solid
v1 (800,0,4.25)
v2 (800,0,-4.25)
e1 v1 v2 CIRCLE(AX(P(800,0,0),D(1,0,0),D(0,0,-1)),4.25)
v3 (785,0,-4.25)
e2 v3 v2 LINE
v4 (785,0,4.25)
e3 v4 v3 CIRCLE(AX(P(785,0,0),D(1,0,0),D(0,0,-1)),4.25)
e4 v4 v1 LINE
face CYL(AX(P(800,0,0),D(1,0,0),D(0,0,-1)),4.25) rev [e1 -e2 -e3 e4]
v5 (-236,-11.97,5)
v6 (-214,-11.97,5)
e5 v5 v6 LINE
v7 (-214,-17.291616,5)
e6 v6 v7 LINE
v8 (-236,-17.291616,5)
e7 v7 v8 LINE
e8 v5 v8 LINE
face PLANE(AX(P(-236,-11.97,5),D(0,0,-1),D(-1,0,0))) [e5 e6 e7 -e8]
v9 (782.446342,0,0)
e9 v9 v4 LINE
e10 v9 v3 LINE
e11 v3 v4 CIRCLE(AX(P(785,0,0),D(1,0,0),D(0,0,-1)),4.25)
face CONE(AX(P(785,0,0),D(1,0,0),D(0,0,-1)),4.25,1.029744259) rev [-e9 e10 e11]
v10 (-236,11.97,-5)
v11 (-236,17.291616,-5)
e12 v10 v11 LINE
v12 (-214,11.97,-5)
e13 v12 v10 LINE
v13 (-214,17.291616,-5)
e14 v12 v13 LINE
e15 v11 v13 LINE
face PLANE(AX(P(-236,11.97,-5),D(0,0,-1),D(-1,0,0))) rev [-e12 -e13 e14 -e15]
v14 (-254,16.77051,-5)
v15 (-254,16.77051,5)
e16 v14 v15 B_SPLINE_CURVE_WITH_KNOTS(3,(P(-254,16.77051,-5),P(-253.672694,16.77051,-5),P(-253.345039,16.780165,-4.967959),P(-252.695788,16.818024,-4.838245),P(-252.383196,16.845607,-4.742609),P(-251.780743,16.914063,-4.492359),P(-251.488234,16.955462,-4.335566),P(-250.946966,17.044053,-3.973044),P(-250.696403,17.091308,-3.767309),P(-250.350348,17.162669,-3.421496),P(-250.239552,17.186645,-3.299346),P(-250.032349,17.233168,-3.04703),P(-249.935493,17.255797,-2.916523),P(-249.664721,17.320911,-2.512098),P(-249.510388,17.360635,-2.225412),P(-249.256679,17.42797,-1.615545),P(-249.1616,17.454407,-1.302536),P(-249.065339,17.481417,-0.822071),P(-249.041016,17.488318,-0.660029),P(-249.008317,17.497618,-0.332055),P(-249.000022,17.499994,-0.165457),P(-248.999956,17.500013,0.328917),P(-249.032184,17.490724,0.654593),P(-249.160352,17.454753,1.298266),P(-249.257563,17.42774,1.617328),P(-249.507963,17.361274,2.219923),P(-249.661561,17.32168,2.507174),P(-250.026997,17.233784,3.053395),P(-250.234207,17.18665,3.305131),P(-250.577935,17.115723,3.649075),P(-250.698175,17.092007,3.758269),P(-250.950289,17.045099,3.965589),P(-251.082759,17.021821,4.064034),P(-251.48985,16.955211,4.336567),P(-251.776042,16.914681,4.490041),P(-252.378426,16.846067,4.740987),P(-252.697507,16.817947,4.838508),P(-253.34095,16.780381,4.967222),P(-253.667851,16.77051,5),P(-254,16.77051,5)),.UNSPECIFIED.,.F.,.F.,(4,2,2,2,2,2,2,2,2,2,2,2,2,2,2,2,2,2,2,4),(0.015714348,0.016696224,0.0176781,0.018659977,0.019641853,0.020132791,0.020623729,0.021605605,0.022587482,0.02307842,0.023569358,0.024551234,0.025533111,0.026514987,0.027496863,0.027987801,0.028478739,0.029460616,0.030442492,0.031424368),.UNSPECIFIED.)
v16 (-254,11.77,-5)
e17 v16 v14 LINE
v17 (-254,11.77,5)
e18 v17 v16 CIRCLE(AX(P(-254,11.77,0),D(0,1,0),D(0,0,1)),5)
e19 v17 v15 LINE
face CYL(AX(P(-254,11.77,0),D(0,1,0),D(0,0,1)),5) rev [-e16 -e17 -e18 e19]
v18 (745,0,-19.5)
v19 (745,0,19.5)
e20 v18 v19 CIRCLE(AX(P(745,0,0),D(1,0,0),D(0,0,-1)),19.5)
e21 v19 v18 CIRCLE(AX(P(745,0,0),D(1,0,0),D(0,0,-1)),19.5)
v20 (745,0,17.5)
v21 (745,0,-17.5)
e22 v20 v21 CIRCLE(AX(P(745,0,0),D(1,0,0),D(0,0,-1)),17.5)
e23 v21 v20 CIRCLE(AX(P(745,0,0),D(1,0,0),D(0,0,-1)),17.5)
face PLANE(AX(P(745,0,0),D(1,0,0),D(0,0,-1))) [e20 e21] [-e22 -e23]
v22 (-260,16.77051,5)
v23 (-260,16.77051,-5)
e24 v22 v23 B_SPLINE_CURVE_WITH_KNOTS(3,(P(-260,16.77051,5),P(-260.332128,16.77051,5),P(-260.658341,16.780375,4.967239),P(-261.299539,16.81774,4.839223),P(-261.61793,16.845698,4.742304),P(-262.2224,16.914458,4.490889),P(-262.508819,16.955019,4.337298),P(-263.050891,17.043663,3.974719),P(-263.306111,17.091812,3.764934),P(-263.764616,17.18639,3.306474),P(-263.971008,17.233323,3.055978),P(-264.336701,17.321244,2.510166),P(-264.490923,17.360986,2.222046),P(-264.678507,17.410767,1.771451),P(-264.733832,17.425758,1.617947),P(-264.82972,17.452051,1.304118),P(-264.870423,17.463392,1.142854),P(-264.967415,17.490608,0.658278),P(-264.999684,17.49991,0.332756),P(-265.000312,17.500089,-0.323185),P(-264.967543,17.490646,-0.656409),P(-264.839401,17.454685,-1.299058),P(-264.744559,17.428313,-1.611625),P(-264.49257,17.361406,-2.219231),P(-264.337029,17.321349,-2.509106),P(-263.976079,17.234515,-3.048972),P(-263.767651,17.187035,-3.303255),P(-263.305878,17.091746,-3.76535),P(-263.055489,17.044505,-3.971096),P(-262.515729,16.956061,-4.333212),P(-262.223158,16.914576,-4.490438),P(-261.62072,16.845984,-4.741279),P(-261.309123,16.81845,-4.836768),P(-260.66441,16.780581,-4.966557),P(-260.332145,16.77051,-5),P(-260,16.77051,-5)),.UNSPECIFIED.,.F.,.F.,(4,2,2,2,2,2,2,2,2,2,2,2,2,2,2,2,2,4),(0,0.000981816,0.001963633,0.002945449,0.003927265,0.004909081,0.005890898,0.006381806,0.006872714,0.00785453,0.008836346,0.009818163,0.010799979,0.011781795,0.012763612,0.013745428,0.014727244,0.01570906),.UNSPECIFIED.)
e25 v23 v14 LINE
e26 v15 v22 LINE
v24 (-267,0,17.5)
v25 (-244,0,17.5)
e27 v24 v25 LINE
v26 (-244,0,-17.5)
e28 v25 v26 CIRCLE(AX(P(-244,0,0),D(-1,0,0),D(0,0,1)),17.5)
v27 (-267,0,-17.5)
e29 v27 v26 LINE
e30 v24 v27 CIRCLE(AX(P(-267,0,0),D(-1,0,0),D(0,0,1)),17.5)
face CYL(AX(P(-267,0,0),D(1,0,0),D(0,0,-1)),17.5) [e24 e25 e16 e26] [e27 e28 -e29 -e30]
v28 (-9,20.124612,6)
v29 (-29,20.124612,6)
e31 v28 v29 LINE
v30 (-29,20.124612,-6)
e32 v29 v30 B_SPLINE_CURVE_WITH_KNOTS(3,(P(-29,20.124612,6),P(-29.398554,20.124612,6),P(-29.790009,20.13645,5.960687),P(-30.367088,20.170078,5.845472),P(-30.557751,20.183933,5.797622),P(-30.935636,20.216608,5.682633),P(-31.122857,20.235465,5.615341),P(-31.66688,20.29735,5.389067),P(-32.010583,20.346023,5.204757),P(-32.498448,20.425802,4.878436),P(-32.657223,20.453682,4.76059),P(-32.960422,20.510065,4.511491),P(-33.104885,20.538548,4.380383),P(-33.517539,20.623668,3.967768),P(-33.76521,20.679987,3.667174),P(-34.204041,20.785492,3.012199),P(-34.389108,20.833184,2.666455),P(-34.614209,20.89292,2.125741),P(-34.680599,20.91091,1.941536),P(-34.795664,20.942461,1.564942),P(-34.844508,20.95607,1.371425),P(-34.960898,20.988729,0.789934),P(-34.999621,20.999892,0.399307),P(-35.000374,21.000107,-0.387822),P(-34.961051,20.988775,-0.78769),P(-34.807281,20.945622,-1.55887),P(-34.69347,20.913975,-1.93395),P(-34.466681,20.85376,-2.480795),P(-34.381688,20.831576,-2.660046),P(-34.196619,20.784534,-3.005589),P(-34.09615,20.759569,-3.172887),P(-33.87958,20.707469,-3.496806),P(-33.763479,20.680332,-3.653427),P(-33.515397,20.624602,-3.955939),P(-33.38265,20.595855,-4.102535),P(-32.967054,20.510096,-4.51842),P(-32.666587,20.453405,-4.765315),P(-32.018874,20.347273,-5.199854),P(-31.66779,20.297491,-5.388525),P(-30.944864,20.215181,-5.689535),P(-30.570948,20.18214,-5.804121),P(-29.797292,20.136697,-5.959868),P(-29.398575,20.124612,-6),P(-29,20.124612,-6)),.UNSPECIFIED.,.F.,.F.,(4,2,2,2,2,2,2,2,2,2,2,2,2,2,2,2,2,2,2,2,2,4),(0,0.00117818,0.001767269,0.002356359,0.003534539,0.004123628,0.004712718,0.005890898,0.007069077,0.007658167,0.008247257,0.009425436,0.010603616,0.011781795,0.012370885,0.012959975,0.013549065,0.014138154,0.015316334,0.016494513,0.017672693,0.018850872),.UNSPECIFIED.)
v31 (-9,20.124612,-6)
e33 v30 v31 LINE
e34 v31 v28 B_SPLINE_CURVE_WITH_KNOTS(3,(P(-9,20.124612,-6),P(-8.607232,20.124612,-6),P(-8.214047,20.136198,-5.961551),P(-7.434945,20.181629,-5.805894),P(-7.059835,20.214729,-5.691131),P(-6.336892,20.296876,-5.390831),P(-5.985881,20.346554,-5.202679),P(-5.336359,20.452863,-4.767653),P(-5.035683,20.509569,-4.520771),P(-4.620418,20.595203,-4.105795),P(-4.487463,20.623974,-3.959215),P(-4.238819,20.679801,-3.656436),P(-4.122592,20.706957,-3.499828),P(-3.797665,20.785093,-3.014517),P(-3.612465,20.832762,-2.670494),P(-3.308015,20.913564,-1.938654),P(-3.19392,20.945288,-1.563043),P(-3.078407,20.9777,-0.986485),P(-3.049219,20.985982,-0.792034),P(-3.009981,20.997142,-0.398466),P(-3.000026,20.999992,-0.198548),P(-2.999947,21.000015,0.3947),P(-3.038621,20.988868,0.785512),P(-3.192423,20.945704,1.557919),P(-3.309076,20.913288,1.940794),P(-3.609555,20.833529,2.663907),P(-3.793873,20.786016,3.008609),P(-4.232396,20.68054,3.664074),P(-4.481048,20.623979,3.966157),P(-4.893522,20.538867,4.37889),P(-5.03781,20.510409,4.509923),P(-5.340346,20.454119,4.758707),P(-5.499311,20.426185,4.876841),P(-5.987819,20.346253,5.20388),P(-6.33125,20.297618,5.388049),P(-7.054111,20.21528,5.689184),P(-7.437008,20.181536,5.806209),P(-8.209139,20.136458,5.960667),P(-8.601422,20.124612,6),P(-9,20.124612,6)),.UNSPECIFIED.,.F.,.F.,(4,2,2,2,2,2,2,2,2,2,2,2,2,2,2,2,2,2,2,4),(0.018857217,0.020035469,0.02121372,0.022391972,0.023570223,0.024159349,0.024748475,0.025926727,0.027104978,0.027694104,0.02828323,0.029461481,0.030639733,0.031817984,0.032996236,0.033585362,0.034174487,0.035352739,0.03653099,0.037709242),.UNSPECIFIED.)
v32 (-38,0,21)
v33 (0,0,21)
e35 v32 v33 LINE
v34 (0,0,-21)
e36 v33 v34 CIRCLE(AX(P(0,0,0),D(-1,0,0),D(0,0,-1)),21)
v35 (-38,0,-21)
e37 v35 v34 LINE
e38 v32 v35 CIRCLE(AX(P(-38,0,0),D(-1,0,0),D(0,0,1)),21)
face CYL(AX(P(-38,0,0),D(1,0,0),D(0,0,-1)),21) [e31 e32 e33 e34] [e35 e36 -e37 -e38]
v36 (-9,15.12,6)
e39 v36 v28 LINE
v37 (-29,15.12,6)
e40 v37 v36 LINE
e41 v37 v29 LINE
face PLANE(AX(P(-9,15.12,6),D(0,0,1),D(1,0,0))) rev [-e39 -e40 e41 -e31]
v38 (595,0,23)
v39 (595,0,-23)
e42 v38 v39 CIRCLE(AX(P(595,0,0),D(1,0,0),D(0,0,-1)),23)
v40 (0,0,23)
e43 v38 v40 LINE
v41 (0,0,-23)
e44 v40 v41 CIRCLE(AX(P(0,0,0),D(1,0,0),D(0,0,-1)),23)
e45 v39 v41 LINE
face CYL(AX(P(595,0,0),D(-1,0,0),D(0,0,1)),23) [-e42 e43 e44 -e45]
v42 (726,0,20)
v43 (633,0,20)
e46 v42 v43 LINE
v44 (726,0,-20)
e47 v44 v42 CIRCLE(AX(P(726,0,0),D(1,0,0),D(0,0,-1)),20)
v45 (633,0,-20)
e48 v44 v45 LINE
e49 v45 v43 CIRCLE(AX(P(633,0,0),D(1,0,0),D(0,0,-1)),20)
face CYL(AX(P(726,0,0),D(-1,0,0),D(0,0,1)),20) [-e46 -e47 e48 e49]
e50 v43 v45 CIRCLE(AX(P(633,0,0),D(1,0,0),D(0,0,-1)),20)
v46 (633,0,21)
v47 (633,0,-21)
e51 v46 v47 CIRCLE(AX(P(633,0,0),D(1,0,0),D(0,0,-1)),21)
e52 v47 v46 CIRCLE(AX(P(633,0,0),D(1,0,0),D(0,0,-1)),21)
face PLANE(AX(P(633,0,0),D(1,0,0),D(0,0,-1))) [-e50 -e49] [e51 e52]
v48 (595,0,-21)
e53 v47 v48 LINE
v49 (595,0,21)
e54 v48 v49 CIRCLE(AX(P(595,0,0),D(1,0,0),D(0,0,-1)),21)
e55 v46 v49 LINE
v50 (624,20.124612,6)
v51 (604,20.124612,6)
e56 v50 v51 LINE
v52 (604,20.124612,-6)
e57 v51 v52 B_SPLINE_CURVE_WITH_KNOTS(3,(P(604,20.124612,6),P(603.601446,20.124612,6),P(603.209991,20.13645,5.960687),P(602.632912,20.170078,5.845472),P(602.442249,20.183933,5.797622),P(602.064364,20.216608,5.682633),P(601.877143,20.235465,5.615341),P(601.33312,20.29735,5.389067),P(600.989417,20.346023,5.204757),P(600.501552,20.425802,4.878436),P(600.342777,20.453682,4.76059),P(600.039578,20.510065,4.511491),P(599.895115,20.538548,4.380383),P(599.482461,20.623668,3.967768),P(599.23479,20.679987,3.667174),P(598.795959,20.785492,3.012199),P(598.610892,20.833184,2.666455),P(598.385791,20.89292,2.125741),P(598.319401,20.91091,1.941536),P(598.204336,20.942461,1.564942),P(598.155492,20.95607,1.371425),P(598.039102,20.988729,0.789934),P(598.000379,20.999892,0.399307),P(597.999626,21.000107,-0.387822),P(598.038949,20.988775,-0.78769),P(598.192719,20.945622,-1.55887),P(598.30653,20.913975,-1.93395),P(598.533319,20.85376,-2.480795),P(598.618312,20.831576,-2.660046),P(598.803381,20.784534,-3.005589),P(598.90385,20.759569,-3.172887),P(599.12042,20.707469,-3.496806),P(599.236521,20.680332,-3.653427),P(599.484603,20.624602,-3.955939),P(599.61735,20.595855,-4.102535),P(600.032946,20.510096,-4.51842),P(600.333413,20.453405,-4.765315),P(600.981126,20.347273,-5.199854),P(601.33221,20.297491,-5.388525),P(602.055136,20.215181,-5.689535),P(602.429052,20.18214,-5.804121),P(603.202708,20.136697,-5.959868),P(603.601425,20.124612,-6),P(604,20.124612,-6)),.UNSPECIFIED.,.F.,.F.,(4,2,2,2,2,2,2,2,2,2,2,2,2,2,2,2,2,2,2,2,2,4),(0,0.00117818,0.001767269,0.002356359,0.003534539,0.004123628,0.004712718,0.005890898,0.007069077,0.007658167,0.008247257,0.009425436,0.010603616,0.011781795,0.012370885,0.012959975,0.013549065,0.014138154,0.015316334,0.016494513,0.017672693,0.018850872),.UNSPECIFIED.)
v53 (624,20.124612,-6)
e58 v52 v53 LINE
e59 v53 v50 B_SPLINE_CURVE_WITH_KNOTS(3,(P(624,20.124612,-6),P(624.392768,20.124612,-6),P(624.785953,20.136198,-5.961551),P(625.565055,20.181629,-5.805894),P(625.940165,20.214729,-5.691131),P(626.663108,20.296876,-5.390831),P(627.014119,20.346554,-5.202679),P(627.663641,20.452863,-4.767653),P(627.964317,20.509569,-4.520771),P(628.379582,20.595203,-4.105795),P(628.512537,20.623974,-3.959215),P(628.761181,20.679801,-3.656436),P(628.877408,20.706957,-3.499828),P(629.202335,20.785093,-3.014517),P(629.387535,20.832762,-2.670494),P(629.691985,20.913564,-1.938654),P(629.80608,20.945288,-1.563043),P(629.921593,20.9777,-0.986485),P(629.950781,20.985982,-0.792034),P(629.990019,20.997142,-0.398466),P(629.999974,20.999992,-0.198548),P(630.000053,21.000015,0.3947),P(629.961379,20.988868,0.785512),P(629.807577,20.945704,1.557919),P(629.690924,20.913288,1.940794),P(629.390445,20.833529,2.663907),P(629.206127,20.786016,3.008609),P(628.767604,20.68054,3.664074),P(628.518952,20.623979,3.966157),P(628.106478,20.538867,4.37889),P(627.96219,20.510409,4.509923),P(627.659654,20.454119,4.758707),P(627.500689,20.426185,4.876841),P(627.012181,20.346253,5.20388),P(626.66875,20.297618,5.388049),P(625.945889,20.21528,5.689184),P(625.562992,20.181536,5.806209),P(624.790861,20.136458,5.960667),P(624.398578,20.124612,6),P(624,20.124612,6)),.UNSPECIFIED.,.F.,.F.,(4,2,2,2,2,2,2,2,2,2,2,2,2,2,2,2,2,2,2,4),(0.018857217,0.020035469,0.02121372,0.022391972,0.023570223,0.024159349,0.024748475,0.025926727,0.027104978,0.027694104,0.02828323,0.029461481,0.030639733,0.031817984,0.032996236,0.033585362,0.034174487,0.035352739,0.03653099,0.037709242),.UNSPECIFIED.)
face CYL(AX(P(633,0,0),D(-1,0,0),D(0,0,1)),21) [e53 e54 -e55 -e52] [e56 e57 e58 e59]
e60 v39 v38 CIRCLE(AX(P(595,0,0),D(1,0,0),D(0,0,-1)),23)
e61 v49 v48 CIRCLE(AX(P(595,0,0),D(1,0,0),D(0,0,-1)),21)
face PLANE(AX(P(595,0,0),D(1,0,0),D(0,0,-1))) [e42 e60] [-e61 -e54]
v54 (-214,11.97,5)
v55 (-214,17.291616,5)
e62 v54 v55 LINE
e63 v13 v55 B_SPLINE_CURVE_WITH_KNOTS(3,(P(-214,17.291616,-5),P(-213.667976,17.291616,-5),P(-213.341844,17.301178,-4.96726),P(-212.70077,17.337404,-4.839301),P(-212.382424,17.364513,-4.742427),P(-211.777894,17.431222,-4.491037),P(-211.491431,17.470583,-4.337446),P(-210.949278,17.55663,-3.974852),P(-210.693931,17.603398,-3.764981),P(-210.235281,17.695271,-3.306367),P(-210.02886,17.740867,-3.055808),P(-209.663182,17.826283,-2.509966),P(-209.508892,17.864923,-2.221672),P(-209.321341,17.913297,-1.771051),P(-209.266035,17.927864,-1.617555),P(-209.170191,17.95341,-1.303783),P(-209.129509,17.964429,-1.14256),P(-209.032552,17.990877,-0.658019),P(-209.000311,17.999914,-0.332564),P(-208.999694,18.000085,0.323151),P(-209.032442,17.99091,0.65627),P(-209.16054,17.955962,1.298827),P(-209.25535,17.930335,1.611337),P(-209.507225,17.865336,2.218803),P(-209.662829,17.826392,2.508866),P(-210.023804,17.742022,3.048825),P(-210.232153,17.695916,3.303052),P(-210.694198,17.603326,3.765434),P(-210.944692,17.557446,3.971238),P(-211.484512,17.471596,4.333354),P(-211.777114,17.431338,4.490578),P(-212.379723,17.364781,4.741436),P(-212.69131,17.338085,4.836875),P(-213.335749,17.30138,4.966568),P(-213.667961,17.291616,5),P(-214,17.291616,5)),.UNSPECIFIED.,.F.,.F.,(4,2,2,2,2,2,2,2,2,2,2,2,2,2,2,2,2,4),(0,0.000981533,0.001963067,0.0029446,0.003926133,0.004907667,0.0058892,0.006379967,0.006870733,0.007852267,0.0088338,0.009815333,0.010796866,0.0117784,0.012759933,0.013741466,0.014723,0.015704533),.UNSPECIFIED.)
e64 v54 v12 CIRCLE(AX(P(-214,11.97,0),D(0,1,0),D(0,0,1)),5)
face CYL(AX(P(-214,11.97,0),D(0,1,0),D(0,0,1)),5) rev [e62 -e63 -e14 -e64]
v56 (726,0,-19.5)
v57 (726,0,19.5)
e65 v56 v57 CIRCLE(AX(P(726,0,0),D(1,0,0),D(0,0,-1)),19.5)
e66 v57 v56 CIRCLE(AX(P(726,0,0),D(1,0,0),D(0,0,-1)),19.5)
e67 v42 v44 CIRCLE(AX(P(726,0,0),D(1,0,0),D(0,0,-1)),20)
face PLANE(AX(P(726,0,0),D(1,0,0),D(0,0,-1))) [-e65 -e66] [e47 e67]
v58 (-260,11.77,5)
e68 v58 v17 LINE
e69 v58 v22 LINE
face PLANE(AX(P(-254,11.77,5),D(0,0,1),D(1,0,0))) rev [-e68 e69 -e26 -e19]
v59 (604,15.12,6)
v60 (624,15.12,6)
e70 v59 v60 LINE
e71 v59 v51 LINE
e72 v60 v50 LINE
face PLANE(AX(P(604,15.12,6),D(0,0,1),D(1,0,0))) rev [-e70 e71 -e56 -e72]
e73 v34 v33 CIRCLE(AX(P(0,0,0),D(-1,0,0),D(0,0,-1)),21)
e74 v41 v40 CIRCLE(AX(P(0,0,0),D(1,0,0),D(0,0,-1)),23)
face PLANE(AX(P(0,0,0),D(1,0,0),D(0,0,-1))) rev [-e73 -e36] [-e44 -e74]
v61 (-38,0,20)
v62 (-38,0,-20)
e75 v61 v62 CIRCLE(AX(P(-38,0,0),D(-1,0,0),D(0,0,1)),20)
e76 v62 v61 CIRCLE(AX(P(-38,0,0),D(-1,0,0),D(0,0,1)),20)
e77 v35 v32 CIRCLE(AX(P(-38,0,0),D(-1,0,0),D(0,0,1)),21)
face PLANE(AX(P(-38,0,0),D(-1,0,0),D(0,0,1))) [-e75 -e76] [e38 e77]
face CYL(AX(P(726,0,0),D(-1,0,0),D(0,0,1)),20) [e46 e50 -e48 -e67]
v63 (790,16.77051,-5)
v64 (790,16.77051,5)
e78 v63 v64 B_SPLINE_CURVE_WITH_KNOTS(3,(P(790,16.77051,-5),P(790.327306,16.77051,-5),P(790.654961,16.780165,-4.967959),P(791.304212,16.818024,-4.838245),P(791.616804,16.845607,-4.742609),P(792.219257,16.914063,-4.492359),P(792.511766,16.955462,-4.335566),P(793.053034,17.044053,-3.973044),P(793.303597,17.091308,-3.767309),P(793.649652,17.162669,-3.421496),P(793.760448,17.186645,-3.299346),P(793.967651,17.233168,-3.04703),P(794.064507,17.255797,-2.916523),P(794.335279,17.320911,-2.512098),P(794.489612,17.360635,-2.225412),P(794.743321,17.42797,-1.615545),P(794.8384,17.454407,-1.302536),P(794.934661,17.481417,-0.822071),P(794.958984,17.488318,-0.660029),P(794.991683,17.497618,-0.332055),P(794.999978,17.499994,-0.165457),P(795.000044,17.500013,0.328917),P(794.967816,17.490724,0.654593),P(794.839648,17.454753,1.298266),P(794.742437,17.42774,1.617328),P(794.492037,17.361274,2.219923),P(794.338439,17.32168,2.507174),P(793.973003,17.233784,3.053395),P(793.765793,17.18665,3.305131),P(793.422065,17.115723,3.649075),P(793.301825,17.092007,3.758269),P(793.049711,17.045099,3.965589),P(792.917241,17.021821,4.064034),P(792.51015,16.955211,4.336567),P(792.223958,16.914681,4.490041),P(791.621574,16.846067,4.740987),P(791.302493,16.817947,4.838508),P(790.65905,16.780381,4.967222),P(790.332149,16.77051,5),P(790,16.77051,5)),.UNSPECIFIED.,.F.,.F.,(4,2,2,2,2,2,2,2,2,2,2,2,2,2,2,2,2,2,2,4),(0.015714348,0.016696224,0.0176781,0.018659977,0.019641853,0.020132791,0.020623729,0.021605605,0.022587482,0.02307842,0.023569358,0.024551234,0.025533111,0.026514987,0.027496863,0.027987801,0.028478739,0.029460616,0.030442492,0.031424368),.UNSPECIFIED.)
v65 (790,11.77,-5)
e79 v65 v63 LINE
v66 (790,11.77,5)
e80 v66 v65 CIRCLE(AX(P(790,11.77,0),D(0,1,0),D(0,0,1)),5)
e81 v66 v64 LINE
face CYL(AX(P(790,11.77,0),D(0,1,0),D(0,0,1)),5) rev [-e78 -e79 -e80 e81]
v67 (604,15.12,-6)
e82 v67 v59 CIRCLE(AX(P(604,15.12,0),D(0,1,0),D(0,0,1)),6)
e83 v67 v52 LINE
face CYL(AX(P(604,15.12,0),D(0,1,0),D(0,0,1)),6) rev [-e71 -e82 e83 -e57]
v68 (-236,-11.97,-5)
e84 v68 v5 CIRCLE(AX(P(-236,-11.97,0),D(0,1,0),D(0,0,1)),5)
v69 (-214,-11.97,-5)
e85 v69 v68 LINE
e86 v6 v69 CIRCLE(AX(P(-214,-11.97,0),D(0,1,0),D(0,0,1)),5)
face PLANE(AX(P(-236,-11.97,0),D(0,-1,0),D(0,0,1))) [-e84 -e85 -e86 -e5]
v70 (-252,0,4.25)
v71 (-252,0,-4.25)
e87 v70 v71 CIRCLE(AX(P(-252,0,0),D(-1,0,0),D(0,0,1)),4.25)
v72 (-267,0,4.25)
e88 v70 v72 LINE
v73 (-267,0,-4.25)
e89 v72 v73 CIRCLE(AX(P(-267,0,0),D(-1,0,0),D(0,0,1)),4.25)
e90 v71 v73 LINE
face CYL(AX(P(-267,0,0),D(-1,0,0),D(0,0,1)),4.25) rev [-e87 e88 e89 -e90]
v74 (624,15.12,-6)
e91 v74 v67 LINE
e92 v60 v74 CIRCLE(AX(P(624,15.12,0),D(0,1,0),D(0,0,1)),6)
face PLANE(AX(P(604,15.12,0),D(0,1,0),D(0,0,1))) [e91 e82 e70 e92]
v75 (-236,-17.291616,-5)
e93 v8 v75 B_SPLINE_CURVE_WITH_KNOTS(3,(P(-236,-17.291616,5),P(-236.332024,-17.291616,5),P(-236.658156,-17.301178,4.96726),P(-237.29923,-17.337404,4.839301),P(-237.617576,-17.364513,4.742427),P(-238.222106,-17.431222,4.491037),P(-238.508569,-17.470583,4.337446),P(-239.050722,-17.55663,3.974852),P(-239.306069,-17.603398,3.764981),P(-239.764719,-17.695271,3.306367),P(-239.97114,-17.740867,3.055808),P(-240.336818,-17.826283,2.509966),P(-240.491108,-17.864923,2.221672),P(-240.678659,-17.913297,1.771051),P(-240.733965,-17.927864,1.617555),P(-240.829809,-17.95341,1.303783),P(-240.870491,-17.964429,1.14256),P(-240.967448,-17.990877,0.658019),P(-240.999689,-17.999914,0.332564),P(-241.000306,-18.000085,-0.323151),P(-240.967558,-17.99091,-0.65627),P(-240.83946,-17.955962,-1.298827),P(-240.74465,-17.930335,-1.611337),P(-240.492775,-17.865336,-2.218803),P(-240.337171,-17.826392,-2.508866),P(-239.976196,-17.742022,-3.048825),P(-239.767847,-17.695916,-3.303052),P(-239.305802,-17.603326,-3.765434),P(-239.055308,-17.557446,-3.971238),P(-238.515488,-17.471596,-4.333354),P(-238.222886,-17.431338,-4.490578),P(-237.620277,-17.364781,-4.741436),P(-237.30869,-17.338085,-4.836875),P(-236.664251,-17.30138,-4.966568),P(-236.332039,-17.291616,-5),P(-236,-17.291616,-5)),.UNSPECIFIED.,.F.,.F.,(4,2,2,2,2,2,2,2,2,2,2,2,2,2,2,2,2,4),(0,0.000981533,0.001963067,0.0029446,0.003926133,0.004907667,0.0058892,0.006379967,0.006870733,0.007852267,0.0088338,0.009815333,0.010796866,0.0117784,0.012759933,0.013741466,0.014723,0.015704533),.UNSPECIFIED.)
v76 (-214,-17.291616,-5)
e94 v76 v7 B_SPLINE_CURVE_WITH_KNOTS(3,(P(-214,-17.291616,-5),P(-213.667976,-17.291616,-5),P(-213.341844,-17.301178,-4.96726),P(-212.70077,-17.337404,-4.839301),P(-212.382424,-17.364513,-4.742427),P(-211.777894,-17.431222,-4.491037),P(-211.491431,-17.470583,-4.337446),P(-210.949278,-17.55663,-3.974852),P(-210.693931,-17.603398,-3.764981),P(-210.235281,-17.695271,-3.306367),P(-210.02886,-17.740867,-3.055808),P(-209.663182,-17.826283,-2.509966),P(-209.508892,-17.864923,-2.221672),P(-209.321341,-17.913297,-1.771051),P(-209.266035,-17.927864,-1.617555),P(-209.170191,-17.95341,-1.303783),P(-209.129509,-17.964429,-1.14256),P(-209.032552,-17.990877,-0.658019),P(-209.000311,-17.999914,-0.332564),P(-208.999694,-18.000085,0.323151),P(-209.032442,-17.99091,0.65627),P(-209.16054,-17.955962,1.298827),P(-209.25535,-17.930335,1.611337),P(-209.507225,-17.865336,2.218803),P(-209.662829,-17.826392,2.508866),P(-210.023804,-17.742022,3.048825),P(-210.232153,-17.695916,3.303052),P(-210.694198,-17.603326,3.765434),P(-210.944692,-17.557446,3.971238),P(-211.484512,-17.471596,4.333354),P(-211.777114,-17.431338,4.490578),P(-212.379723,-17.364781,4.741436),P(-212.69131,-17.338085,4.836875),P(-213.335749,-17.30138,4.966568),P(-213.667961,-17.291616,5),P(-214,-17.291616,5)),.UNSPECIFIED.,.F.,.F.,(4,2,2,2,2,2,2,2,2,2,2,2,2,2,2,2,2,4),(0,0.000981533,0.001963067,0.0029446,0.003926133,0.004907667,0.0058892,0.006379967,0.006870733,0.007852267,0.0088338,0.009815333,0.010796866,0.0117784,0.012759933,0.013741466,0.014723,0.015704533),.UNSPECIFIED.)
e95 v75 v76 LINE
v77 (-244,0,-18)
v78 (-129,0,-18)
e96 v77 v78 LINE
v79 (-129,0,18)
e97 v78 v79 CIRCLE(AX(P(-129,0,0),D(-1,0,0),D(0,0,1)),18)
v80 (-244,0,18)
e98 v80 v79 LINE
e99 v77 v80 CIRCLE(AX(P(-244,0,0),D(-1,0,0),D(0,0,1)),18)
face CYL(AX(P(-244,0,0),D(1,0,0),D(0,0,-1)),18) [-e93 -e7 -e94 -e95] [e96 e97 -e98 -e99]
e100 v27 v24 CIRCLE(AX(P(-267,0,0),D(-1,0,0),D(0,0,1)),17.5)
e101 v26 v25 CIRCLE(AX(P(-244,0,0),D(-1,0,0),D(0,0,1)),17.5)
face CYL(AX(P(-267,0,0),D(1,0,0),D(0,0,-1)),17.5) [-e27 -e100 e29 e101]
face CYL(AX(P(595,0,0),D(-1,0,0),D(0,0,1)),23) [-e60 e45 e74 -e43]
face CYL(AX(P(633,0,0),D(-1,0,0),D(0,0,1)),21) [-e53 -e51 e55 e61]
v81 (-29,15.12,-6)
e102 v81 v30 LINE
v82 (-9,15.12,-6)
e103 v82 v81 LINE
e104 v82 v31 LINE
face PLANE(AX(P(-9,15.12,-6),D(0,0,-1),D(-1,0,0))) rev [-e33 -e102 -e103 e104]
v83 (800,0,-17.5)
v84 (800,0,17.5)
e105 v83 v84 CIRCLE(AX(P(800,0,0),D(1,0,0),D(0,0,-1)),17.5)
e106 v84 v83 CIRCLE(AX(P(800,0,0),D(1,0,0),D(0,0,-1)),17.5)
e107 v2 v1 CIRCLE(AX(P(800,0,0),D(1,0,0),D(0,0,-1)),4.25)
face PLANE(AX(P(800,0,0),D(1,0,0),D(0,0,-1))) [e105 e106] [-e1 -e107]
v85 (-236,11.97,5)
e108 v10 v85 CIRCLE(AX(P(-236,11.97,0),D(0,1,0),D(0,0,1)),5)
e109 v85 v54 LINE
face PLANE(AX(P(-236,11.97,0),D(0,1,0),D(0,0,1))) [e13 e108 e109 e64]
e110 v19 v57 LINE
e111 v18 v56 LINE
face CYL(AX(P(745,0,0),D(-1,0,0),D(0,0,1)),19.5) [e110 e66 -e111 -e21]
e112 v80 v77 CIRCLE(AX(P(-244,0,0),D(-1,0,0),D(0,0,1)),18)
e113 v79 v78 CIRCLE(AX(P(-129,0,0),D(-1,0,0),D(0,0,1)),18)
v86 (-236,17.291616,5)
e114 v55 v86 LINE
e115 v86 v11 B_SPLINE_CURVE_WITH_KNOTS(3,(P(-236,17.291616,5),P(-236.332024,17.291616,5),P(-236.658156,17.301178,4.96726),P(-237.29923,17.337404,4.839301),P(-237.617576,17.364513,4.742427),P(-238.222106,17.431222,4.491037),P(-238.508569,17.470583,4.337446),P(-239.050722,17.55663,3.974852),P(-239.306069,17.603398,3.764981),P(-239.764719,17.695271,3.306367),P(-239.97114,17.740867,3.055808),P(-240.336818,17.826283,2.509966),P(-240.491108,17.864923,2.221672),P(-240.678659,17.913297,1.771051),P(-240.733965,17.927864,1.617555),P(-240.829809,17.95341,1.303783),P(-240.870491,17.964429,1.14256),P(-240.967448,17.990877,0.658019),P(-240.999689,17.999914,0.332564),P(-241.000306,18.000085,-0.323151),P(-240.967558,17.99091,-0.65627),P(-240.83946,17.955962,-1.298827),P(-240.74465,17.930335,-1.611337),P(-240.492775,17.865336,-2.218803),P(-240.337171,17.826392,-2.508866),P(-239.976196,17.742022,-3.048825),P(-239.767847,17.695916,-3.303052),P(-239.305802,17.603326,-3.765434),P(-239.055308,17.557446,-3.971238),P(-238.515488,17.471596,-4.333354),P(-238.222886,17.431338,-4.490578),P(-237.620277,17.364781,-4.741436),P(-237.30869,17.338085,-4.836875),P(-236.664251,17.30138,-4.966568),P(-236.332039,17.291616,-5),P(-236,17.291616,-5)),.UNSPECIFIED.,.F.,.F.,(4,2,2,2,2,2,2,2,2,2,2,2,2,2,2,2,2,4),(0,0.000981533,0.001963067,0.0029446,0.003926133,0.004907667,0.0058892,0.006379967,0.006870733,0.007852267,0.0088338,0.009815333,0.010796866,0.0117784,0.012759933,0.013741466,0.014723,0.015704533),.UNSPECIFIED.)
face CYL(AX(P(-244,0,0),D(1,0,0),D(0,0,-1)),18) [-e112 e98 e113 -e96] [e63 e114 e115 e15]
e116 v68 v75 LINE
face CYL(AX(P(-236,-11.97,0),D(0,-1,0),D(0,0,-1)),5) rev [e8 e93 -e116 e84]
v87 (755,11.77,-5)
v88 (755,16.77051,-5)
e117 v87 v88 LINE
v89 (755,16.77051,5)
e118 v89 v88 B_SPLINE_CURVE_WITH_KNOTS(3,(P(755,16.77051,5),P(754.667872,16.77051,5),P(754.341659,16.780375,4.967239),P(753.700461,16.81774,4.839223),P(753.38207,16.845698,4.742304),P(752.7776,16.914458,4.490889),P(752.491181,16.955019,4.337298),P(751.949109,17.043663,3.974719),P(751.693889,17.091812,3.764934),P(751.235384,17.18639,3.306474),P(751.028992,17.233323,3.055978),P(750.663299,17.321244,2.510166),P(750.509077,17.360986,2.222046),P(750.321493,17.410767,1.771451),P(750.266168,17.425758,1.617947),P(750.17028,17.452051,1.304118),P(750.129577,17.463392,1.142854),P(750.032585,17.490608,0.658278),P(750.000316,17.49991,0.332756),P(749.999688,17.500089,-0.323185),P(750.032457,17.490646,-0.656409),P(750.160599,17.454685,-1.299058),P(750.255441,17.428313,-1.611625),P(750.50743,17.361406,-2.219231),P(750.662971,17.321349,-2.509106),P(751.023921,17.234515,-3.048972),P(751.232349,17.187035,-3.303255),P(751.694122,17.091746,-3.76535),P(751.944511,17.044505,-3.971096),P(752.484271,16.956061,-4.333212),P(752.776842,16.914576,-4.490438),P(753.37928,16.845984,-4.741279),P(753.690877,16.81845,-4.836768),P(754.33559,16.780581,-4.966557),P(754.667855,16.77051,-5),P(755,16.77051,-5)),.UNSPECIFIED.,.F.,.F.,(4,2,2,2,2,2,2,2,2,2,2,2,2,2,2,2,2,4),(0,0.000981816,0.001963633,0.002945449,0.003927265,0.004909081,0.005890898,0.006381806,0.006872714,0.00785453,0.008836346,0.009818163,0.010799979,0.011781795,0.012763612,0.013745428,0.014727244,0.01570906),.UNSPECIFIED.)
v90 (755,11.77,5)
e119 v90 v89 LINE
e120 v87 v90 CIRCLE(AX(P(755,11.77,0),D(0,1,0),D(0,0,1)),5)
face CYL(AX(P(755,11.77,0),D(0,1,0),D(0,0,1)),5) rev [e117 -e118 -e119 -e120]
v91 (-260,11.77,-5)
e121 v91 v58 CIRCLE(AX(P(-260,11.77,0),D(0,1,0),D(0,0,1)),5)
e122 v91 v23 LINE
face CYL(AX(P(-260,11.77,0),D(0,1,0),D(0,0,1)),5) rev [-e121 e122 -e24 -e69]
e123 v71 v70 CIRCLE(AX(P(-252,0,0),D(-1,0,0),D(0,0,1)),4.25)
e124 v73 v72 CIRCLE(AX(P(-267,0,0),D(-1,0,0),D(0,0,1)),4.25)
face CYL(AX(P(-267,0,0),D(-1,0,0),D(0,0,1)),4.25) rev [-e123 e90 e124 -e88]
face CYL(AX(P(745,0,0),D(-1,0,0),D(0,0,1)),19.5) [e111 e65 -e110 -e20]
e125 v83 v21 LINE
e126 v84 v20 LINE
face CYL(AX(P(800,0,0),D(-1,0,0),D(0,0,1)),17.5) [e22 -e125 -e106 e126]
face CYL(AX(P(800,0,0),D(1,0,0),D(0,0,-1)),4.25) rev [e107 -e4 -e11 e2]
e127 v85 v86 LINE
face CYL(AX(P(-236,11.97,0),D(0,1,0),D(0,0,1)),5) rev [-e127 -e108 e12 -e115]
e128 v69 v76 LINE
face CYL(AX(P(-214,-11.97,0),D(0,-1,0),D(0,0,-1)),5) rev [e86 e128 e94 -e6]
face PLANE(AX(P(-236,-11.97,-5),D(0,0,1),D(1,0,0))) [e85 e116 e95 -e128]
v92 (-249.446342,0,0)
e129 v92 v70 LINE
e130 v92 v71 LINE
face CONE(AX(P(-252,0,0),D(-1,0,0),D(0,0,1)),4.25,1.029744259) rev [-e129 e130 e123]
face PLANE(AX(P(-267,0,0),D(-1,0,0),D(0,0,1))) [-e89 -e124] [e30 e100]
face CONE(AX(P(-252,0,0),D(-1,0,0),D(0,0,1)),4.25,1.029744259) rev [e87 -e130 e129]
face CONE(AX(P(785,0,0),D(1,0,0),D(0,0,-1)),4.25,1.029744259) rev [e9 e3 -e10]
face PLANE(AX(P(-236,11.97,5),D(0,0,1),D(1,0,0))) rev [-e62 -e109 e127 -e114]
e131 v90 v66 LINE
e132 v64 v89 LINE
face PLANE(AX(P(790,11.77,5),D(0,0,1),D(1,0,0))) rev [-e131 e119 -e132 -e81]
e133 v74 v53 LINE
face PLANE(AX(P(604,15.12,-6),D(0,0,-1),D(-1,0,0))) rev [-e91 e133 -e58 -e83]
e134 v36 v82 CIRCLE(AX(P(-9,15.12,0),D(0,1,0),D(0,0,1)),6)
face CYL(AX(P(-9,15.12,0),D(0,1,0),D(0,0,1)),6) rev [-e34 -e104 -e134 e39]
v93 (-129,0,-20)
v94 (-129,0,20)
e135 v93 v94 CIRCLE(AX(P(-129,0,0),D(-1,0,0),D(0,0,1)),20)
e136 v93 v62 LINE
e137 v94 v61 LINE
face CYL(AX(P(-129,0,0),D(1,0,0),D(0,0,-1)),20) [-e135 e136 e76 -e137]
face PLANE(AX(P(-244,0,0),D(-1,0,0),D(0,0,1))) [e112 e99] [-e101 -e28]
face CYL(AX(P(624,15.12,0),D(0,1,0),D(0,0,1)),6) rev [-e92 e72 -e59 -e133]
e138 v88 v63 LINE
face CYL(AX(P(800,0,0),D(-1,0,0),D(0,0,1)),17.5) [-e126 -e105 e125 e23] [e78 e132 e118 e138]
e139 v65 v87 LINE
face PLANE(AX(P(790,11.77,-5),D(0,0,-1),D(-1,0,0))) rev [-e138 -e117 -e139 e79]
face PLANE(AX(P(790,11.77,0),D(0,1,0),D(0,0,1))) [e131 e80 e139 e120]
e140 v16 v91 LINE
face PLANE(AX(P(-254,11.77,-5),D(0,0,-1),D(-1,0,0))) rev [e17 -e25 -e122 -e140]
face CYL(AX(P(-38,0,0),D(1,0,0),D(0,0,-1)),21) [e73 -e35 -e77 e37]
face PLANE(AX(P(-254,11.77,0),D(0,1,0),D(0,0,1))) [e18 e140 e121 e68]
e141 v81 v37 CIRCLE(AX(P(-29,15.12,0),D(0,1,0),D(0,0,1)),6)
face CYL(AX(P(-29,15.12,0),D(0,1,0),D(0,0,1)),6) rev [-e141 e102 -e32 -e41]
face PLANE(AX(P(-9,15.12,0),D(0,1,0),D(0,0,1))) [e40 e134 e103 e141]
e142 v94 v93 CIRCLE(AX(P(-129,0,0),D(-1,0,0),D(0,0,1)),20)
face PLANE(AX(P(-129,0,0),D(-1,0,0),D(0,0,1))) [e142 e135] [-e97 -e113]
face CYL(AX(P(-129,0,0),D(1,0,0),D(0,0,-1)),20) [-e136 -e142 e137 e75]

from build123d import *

# Parameters (mm, degrees)
SKETCH_1_R              = 23
EXTRUDE_1_DEPTH         = 595
SKETCH_2_R              = 21
EXTRUDE_2_DEPTH         = 38
SKETCH_3_R              = 20
EXTRUDE_3_DEPTH         = 91
SKETCH_4_R              = 18
EXTRUDE_4_DEPTH         = 115
SKETCH_5_R              = 17.5
EXTRUDE_5_DEPTH         = 23
EXTRUDE_START           = 38
SKETCH_7_R              = 21
EXTRUDE_6_DEPTH         = 38
CUT_EXTRUDE_2_DEPTH     = 5.88
CUT_EXTRUDE_3_DEPTH     = 6.03
EXTRUDE_START_2         = 93
SKETCH_10_R             = 20
EXTRUDE_7_DEPTH         = 93
SKETCH_11_R             = 19.5
EXTRUDE_8_DEPTH         = 19
EXTRUDE_START_3         = 55
SKETCH_12_R             = 17.5
EXTRUDE_9_DEPTH         = 55
CUT_EXTRUDE_4_DEPTH     = 5.73
HOLE_WIZARD_M10_1_D     = 8.5
HOLE_WIZARD_M10_1_DEPTH = 15
HOLE_WIZARD_M10_1_TIP   = 2.553657631
HOLE_WIZARD_M10_2_D     = 8.5
HOLE_WIZARD_M10_2_DEPTH = 15
HOLE_WIZARD_M10_2_TIP   = 2.553657631


with BuildPart() as part:
    # 草图1 → 凸台-拉伸1 (new body)
    with BuildSketch(Plane(origin=(0, 0, 0), x_dir=(0, 0, -1), z_dir=(1, 0, 0))):
        Circle(SKETCH_1_R)
    extrude(amount=EXTRUDE_1_DEPTH)

    # 草图2 → 凸台-拉伸2 (add)
    with BuildSketch(Plane.ZY):
        with Locations(Location((0, 0, 0), (0, 0, 180))):
            Circle(SKETCH_2_R)
    extrude(amount=EXTRUDE_2_DEPTH)

    # 草图3 → 凸台-拉伸3 (add)
    with BuildSketch(Plane.ZY.offset(38)):
        Circle(SKETCH_3_R)
    extrude(amount=EXTRUDE_3_DEPTH)

    # 草图4 → 凸台-拉伸4 (add)
    with BuildSketch(Plane.ZY.offset(129)):
        Circle(SKETCH_4_R)
    extrude(amount=EXTRUDE_4_DEPTH)

    # 草图5 → 凸台-拉伸5 (add)
    with BuildSketch(Plane.ZY.offset(244)):
        Circle(SKETCH_5_R)
    extrude(amount=EXTRUDE_5_DEPTH)

    # 草图7 → 凸台-拉伸6 (add)
    with BuildSketch(Plane(origin=(595, 0, 0), x_dir=(0, 0, -1), z_dir=(1, 0, 0)).offset(EXTRUDE_START)):
        Circle(SKETCH_7_R)
    extrude(amount=-EXTRUDE_6_DEPTH)

    # 草图6 → 切除-拉伸2 (cut)
    with BuildSketch(Plane(origin=(0, 21, 0), x_dir=(1, 0, 0), z_dir=(0, 1, 0))):
        with BuildLine():
            Line((-9, -6), (-29, -6))
            ThreePointArc((-29, -6), (-35, 0), (-29, 6))
            Line((-29, 6), (-9, 6))
            ThreePointArc((-9, 6), (-3, 0), (-9, -6))
        make_face()
        with BuildLine():
            Line((604, 6), (624, 6))
            ThreePointArc((624, 6), (630, 0), (624, -6))
            Line((624, -6), (604, -6))
            ThreePointArc((604, -6), (598, 0), (604, 6))
        make_face()
    extrude(amount=-CUT_EXTRUDE_2_DEPTH, mode=Mode.SUBTRACT)

    # 草图9 → 切除-拉伸3 (cut)
    with BuildSketch(Plane(origin=(0, 18, 0), x_dir=(1, 0, 0), z_dir=(0, 1, 0))):
        with BuildLine():
            Line((-236, 5), (-214, 5))
            ThreePointArc((-214, 5), (-209, 0), (-214, -5))
            Line((-214, -5), (-236, -5))
            ThreePointArc((-236, -5), (-241, 0), (-236, 5))
        make_face()
    cut_extrude_3 = extrude(amount=-CUT_EXTRUDE_3_DEPTH, mode=Mode.SUBTRACT)

    # 草图10 → 凸台-拉伸7 (add)
    with BuildSketch(Plane(origin=(633, 0, 0), x_dir=(0, 0, -1), z_dir=(1, 0, 0)).offset(EXTRUDE_START_2)):
        with Locations(Location((0, 0, 0), (0, 0, 180))):
            Circle(SKETCH_10_R)
    extrude(amount=-EXTRUDE_7_DEPTH)

    # 草图11 → 凸台-拉伸8 (add)
    with BuildSketch(Plane(origin=(726, 0, 0), x_dir=(0, 0, -1), z_dir=(1, 0, 0))):
        Circle(SKETCH_11_R)
    extrude(amount=EXTRUDE_8_DEPTH)

    # 草图12 → 凸台-拉伸9 (add)
    with BuildSketch(Plane(origin=(745, 0, 0), x_dir=(0, 0, -1), z_dir=(1, 0, 0)).offset(EXTRUDE_START_3)):
        with Locations(Location((0, 0, 0), (0, 0, 180))):
            Circle(SKETCH_12_R)
    extrude(amount=-EXTRUDE_9_DEPTH)

    # 草图13 → 切除-拉伸4 (cut)
    with BuildSketch(Plane(origin=(0, 17.5, 0), x_dir=(1, 0, 0), z_dir=(0, 1, 0))):
        with BuildLine():
            Line((-254, -5), (-260, -5))
            ThreePointArc((-260, -5), (-265, 0), (-260, 5))
            Line((-260, 5), (-254, 5))
            ThreePointArc((-254, 5), (-249, 0), (-254, -5))
        make_face()
        with BuildLine():
            Line((790, -5), (755, -5))
            ThreePointArc((755, -5), (750, 0), (755, 5))
            Line((755, 5), (790, 5))
            ThreePointArc((790, 5), (795, 0), (790, -5))
        make_face()
    extrude(amount=-CUT_EXTRUDE_4_DEPTH, mode=Mode.SUBTRACT)

    # M10 螺纹孔1
    with Locations(Plane.ZY.offset(267)):
        with Locations((0, 0)):
            Hole(HOLE_WIZARD_M10_1_D / 2, depth=HOLE_WIZARD_M10_1_DEPTH)
            with Locations((0, 0, -(HOLE_WIZARD_M10_1_DEPTH + HOLE_WIZARD_M10_1_TIP / 2))):  # 118° drill point
                Cone(0, HOLE_WIZARD_M10_1_D / 2, HOLE_WIZARD_M10_1_TIP, mode=Mode.SUBTRACT)

    # M10 螺纹孔2
    with Locations(Plane(origin=(800, 0, 0), x_dir=(0, 0, -1), z_dir=(1, 0, 0))):
        with Locations((0, 0)):
            Hole(HOLE_WIZARD_M10_2_D / 2, depth=HOLE_WIZARD_M10_2_DEPTH)
            with Locations((0, 0, -(HOLE_WIZARD_M10_2_DEPTH + HOLE_WIZARD_M10_2_TIP / 2))):  # 118° drill point
                Cone(0, HOLE_WIZARD_M10_2_D / 2, HOLE_WIZARD_M10_2_TIP, mode=Mode.SUBTRACT)

    # 镜向1: 切除-拉伸3 across plane
    add(cut_extrude_3.mirror(Plane.ZX), mode=Mode.SUBTRACT)


solid = part.part
